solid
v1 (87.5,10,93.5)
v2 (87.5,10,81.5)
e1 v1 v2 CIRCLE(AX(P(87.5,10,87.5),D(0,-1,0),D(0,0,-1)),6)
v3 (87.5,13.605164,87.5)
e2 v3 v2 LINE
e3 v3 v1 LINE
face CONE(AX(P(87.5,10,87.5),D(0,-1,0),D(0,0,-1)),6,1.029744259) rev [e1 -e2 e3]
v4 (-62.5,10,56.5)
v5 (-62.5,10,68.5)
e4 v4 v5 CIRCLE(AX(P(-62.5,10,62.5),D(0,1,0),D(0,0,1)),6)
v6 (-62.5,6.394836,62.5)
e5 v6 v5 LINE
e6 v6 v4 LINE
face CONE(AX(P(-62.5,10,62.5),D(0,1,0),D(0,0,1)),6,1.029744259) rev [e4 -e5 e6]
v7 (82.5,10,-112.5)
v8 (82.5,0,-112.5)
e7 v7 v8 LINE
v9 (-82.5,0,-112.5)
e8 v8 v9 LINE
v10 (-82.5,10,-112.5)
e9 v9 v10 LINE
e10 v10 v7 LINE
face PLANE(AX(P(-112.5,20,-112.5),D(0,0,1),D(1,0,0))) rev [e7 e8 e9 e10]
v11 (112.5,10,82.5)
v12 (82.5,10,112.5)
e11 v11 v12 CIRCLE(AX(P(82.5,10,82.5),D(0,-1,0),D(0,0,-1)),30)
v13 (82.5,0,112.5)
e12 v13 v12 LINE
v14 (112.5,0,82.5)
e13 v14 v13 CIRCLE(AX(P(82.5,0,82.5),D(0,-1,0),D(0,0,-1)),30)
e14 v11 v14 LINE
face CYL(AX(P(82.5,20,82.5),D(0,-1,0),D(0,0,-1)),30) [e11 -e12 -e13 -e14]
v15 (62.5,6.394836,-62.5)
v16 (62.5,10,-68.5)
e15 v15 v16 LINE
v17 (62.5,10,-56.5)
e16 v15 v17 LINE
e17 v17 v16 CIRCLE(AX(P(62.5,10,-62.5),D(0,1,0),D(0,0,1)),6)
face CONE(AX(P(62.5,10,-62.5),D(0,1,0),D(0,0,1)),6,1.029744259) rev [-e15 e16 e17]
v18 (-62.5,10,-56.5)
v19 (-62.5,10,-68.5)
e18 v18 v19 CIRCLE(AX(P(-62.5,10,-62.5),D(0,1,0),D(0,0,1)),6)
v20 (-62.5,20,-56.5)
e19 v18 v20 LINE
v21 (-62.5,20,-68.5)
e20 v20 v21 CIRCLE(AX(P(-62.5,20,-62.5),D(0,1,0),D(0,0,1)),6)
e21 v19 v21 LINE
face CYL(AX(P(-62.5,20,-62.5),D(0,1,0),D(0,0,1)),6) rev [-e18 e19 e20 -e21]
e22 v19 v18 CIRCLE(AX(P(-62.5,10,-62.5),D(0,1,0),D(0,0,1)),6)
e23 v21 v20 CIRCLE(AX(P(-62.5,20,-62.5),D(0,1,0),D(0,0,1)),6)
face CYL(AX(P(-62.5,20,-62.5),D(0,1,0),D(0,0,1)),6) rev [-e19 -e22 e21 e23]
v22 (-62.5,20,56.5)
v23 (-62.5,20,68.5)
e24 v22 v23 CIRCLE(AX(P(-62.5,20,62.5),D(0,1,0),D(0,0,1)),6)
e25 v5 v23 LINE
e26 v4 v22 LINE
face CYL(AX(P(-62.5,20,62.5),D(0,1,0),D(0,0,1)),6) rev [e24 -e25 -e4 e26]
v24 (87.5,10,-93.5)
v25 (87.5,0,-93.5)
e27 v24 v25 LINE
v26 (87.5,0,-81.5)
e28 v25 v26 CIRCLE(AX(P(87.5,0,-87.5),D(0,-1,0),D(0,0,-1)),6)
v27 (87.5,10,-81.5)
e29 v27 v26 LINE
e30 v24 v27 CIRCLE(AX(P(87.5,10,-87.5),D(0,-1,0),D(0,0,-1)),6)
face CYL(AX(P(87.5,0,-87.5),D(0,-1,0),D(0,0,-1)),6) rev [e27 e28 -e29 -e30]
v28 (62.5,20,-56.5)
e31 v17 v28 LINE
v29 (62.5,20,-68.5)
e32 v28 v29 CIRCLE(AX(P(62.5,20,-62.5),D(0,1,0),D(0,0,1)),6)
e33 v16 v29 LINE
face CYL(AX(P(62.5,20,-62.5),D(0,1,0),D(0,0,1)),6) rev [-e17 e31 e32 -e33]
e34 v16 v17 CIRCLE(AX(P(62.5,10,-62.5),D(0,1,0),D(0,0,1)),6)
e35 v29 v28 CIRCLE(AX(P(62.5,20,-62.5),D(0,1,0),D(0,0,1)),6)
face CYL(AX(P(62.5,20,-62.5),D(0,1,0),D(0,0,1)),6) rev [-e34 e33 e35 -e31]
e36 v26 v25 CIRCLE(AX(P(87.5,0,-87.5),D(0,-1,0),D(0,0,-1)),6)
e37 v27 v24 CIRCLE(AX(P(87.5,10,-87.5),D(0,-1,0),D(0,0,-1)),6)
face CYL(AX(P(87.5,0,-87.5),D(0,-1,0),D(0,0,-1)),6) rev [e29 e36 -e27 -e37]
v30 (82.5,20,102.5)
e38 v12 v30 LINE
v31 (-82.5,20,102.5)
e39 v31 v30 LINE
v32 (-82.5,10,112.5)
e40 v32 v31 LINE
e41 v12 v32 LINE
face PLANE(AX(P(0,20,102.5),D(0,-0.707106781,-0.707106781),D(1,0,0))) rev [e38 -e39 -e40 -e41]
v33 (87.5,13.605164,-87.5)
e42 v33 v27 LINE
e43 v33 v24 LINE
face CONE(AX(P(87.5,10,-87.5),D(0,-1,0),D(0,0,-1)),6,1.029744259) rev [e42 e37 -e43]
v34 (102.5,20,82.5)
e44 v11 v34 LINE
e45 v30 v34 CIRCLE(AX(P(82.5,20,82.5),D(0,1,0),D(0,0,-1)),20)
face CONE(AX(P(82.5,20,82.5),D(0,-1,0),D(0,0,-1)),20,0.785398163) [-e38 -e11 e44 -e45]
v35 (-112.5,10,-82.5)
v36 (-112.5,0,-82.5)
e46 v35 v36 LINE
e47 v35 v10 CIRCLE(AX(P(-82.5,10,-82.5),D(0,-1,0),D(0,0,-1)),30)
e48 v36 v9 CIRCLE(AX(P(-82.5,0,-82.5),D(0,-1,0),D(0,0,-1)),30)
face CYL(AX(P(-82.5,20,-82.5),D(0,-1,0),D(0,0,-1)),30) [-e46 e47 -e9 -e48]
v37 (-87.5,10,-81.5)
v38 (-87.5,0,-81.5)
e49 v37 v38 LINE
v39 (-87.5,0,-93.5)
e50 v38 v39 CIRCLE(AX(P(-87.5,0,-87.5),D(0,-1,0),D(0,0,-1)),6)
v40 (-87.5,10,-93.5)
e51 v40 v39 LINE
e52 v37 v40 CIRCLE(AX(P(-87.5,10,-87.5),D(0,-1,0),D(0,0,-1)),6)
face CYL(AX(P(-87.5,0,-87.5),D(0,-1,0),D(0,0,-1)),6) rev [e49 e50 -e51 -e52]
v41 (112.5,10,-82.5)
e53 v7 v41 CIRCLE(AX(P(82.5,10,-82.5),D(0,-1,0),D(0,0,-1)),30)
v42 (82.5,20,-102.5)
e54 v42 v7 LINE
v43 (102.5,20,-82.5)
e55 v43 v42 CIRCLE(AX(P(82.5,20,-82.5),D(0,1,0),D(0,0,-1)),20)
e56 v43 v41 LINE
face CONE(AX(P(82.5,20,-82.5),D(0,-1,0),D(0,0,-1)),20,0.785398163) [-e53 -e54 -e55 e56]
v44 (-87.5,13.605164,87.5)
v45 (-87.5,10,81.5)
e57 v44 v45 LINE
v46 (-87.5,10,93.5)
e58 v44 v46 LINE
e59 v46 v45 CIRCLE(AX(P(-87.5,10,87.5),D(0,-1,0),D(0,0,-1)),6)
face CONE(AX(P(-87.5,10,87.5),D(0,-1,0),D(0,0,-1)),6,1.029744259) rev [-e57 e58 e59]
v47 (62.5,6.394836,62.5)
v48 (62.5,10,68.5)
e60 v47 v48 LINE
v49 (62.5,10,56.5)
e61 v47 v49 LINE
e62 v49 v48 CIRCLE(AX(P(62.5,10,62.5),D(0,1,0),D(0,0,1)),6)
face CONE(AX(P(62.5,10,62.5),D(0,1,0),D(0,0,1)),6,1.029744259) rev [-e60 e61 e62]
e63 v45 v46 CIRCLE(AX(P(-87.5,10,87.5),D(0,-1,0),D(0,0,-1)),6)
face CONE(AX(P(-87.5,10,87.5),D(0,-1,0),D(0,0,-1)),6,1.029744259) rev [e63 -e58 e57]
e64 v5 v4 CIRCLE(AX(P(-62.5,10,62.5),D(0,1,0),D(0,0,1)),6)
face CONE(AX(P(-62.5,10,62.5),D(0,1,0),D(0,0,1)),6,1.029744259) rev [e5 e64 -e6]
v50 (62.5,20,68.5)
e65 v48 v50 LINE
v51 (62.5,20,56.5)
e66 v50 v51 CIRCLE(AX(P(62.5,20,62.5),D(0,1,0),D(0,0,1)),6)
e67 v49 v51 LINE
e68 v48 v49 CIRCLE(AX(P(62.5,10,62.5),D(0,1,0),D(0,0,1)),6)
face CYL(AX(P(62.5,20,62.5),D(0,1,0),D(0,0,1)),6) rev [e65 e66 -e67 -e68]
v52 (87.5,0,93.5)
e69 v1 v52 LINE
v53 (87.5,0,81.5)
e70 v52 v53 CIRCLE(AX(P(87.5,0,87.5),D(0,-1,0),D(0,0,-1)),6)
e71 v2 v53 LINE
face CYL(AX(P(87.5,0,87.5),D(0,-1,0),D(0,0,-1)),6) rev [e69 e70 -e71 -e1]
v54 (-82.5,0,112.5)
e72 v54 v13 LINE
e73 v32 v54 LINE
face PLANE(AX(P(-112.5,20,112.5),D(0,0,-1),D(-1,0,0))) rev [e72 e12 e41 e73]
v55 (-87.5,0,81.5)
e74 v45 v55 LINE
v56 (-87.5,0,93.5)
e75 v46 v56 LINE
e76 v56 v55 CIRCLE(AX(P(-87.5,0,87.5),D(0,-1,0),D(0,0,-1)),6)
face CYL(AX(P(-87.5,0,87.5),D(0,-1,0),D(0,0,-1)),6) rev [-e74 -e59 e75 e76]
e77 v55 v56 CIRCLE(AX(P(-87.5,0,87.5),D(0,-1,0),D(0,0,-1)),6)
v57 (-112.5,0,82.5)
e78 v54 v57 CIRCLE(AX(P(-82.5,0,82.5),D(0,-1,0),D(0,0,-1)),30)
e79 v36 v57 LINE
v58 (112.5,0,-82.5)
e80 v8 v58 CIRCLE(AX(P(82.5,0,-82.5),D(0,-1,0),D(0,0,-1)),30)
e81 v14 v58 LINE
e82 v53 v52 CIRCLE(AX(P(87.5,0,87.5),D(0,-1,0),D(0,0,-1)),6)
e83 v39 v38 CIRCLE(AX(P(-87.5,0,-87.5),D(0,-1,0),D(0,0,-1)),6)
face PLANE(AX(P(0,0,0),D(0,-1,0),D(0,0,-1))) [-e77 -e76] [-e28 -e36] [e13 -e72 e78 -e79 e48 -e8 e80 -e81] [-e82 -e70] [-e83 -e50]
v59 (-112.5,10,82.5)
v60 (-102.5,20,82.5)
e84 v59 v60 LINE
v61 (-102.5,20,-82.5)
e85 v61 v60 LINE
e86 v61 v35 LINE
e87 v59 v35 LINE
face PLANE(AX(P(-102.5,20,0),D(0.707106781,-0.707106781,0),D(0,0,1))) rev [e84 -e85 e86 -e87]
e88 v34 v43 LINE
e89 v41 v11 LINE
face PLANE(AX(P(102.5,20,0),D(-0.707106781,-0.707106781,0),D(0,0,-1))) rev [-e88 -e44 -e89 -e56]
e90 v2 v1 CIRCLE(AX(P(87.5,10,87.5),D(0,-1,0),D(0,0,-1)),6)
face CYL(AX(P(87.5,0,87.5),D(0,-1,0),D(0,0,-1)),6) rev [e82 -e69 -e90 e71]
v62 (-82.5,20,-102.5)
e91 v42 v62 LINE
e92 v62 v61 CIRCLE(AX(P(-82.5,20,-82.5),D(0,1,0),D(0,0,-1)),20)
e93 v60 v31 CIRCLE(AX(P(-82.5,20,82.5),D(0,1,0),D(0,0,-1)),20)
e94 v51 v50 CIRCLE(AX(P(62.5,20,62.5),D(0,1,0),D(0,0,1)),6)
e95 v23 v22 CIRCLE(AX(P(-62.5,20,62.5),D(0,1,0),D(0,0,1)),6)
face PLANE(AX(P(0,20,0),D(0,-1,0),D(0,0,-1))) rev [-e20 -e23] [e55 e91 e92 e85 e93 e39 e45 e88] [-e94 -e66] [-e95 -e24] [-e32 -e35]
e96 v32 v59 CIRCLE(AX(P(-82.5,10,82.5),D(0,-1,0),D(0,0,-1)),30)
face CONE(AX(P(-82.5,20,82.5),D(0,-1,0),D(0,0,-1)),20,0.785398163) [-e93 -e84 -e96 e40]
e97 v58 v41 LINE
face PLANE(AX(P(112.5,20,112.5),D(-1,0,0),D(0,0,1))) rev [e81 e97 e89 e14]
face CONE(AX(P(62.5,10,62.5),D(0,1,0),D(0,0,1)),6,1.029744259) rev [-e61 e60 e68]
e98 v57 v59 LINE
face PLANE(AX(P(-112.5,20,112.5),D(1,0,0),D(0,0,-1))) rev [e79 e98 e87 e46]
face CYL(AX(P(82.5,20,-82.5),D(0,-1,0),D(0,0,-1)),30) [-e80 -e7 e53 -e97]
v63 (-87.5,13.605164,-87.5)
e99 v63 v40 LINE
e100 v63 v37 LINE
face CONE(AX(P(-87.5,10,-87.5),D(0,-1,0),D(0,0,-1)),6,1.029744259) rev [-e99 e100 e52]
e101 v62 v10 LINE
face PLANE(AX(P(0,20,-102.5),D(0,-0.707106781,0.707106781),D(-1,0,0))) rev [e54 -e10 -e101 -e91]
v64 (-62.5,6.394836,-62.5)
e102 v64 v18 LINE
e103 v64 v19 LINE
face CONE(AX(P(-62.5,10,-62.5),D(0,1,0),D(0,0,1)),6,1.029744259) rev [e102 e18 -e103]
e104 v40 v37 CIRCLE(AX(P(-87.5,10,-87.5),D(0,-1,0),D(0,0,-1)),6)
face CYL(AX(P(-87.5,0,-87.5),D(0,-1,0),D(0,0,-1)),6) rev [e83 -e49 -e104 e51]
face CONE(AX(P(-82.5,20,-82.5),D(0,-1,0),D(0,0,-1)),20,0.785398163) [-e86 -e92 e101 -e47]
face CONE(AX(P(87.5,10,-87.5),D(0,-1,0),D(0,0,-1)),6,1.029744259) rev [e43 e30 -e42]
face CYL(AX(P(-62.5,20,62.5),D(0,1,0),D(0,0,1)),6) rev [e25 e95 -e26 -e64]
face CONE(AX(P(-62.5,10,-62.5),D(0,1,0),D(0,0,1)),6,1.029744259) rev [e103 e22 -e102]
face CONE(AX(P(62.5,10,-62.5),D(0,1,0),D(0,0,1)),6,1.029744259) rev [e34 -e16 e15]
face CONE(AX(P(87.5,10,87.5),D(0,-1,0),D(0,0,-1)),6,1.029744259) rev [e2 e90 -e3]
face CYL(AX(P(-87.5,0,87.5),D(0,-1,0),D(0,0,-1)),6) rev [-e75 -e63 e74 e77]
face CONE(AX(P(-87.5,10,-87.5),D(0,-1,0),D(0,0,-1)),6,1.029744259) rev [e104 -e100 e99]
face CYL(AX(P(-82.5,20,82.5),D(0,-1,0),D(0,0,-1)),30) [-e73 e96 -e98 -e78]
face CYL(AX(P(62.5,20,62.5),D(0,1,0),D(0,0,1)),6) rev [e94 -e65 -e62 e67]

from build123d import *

# Parameters (mm, degrees)
BASE_PLATE_SKETCH_225X225_W        = 225
BASE_PLATE_SKETCH_225X225_H        = 225
BASE_PLATE_225X225X20_DEPTH        = 20
CORNER_FILLETS_R30_R               = 30
EDGE_CHAMFER_10X45_SIZE            = 10
DOWEL_HOLES_12_ON_125_LAYOUT_D     = 12
DOWEL_HOLES_12_ON_125_LAYOUT_DEPTH = 10
DOWEL_HOLES_12_ON_125_LAYOUT_TIP   = 3.605163714
DOWEL_HOLES_12_ON_175_LAYOUT_D     = 12
DOWEL_HOLES_12_ON_175_LAYOUT_DEPTH = 10
DOWEL_HOLES_12_ON_175_LAYOUT_TIP   = 3.605163714


with BuildPart() as part:
    # Base Plate Sketch 225x225 → Base Plate 225x225x20 (new body)
    with BuildSketch(Plane(origin=(0, 0, 0), x_dir=(1, 0, 0), z_dir=(0, 1, 0))):
        Rectangle(BASE_PLATE_SKETCH_225X225_W, BASE_PLATE_SKETCH_225X225_H)
    extrude(amount=BASE_PLATE_225X225X20_DEPTH)

    # Corner Fillets R30
    corner_fillets_r30_edges = [part.edges().sort_by_distance(p)[0] for p in [
        (112.5, 10, 112.5),
        (-112.5, 10, 112.5),
        (-112.5, 10, -112.5),
        (112.5, 10, -112.5),
    ]]
    fillet(corner_fillets_r30_edges, radius=CORNER_FILLETS_R30_R)

    # Edge Chamfer 10x45
    edge_chamfer_10x45_edges = [part.edges().sort_by_distance(p)[0] for p in [
        (-112.5, 20, 0),
        (0, 20, -112.5),
        (112.5, 20, 0),
        (0, 20, 112.5),
        (-103.713203436, 20, 103.713203436),
        (103.713203436, 20, 103.713203436),
        (103.713203436, 20, -103.713203436),
        (-103.713203436, 20, -103.713203436),
    ]]
    chamfer(edge_chamfer_10x45_edges, length=EDGE_CHAMFER_10X45_SIZE)

    # Dowel Holes Ø12 on 125 Layout
    with Locations(Plane(origin=(62.5, 20, 62.5), x_dir=(0, 0, 1), z_dir=(0, 1, 0))):
        with Locations((0, 0), (0, -125), (-125, -125), (-125, 0)):
            Hole(DOWEL_HOLES_12_ON_125_LAYOUT_D / 2, depth=DOWEL_HOLES_12_ON_125_LAYOUT_DEPTH)
            with Locations((0, 0, -(DOWEL_HOLES_12_ON_125_LAYOUT_DEPTH + DOWEL_HOLES_12_ON_125_LAYOUT_TIP / 2))):  # 118° drill point
                Cone(0, DOWEL_HOLES_12_ON_125_LAYOUT_D / 2, DOWEL_HOLES_12_ON_125_LAYOUT_TIP, mode=Mode.SUBTRACT)

    # Dowel Holes Ø12 on 175 Layout
    with Locations(Plane(origin=(-87.5, 0, 87.5), x_dir=(0, 0, -1), z_dir=(0, -1, 0))):
        with Locations((0, 0), (0, 175), (175, 175), (175, 0)):
            Hole(DOWEL_HOLES_12_ON_175_LAYOUT_D / 2, depth=DOWEL_HOLES_12_ON_175_LAYOUT_DEPTH)
            with Locations((0, 0, -(DOWEL_HOLES_12_ON_175_LAYOUT_DEPTH + DOWEL_HOLES_12_ON_175_LAYOUT_TIP / 2))):  # 118° drill point
                Cone(0, DOWEL_HOLES_12_ON_175_LAYOUT_D / 2, DOWEL_HOLES_12_ON_175_LAYOUT_TIP, mode=Mode.SUBTRACT)


solid = part.part
